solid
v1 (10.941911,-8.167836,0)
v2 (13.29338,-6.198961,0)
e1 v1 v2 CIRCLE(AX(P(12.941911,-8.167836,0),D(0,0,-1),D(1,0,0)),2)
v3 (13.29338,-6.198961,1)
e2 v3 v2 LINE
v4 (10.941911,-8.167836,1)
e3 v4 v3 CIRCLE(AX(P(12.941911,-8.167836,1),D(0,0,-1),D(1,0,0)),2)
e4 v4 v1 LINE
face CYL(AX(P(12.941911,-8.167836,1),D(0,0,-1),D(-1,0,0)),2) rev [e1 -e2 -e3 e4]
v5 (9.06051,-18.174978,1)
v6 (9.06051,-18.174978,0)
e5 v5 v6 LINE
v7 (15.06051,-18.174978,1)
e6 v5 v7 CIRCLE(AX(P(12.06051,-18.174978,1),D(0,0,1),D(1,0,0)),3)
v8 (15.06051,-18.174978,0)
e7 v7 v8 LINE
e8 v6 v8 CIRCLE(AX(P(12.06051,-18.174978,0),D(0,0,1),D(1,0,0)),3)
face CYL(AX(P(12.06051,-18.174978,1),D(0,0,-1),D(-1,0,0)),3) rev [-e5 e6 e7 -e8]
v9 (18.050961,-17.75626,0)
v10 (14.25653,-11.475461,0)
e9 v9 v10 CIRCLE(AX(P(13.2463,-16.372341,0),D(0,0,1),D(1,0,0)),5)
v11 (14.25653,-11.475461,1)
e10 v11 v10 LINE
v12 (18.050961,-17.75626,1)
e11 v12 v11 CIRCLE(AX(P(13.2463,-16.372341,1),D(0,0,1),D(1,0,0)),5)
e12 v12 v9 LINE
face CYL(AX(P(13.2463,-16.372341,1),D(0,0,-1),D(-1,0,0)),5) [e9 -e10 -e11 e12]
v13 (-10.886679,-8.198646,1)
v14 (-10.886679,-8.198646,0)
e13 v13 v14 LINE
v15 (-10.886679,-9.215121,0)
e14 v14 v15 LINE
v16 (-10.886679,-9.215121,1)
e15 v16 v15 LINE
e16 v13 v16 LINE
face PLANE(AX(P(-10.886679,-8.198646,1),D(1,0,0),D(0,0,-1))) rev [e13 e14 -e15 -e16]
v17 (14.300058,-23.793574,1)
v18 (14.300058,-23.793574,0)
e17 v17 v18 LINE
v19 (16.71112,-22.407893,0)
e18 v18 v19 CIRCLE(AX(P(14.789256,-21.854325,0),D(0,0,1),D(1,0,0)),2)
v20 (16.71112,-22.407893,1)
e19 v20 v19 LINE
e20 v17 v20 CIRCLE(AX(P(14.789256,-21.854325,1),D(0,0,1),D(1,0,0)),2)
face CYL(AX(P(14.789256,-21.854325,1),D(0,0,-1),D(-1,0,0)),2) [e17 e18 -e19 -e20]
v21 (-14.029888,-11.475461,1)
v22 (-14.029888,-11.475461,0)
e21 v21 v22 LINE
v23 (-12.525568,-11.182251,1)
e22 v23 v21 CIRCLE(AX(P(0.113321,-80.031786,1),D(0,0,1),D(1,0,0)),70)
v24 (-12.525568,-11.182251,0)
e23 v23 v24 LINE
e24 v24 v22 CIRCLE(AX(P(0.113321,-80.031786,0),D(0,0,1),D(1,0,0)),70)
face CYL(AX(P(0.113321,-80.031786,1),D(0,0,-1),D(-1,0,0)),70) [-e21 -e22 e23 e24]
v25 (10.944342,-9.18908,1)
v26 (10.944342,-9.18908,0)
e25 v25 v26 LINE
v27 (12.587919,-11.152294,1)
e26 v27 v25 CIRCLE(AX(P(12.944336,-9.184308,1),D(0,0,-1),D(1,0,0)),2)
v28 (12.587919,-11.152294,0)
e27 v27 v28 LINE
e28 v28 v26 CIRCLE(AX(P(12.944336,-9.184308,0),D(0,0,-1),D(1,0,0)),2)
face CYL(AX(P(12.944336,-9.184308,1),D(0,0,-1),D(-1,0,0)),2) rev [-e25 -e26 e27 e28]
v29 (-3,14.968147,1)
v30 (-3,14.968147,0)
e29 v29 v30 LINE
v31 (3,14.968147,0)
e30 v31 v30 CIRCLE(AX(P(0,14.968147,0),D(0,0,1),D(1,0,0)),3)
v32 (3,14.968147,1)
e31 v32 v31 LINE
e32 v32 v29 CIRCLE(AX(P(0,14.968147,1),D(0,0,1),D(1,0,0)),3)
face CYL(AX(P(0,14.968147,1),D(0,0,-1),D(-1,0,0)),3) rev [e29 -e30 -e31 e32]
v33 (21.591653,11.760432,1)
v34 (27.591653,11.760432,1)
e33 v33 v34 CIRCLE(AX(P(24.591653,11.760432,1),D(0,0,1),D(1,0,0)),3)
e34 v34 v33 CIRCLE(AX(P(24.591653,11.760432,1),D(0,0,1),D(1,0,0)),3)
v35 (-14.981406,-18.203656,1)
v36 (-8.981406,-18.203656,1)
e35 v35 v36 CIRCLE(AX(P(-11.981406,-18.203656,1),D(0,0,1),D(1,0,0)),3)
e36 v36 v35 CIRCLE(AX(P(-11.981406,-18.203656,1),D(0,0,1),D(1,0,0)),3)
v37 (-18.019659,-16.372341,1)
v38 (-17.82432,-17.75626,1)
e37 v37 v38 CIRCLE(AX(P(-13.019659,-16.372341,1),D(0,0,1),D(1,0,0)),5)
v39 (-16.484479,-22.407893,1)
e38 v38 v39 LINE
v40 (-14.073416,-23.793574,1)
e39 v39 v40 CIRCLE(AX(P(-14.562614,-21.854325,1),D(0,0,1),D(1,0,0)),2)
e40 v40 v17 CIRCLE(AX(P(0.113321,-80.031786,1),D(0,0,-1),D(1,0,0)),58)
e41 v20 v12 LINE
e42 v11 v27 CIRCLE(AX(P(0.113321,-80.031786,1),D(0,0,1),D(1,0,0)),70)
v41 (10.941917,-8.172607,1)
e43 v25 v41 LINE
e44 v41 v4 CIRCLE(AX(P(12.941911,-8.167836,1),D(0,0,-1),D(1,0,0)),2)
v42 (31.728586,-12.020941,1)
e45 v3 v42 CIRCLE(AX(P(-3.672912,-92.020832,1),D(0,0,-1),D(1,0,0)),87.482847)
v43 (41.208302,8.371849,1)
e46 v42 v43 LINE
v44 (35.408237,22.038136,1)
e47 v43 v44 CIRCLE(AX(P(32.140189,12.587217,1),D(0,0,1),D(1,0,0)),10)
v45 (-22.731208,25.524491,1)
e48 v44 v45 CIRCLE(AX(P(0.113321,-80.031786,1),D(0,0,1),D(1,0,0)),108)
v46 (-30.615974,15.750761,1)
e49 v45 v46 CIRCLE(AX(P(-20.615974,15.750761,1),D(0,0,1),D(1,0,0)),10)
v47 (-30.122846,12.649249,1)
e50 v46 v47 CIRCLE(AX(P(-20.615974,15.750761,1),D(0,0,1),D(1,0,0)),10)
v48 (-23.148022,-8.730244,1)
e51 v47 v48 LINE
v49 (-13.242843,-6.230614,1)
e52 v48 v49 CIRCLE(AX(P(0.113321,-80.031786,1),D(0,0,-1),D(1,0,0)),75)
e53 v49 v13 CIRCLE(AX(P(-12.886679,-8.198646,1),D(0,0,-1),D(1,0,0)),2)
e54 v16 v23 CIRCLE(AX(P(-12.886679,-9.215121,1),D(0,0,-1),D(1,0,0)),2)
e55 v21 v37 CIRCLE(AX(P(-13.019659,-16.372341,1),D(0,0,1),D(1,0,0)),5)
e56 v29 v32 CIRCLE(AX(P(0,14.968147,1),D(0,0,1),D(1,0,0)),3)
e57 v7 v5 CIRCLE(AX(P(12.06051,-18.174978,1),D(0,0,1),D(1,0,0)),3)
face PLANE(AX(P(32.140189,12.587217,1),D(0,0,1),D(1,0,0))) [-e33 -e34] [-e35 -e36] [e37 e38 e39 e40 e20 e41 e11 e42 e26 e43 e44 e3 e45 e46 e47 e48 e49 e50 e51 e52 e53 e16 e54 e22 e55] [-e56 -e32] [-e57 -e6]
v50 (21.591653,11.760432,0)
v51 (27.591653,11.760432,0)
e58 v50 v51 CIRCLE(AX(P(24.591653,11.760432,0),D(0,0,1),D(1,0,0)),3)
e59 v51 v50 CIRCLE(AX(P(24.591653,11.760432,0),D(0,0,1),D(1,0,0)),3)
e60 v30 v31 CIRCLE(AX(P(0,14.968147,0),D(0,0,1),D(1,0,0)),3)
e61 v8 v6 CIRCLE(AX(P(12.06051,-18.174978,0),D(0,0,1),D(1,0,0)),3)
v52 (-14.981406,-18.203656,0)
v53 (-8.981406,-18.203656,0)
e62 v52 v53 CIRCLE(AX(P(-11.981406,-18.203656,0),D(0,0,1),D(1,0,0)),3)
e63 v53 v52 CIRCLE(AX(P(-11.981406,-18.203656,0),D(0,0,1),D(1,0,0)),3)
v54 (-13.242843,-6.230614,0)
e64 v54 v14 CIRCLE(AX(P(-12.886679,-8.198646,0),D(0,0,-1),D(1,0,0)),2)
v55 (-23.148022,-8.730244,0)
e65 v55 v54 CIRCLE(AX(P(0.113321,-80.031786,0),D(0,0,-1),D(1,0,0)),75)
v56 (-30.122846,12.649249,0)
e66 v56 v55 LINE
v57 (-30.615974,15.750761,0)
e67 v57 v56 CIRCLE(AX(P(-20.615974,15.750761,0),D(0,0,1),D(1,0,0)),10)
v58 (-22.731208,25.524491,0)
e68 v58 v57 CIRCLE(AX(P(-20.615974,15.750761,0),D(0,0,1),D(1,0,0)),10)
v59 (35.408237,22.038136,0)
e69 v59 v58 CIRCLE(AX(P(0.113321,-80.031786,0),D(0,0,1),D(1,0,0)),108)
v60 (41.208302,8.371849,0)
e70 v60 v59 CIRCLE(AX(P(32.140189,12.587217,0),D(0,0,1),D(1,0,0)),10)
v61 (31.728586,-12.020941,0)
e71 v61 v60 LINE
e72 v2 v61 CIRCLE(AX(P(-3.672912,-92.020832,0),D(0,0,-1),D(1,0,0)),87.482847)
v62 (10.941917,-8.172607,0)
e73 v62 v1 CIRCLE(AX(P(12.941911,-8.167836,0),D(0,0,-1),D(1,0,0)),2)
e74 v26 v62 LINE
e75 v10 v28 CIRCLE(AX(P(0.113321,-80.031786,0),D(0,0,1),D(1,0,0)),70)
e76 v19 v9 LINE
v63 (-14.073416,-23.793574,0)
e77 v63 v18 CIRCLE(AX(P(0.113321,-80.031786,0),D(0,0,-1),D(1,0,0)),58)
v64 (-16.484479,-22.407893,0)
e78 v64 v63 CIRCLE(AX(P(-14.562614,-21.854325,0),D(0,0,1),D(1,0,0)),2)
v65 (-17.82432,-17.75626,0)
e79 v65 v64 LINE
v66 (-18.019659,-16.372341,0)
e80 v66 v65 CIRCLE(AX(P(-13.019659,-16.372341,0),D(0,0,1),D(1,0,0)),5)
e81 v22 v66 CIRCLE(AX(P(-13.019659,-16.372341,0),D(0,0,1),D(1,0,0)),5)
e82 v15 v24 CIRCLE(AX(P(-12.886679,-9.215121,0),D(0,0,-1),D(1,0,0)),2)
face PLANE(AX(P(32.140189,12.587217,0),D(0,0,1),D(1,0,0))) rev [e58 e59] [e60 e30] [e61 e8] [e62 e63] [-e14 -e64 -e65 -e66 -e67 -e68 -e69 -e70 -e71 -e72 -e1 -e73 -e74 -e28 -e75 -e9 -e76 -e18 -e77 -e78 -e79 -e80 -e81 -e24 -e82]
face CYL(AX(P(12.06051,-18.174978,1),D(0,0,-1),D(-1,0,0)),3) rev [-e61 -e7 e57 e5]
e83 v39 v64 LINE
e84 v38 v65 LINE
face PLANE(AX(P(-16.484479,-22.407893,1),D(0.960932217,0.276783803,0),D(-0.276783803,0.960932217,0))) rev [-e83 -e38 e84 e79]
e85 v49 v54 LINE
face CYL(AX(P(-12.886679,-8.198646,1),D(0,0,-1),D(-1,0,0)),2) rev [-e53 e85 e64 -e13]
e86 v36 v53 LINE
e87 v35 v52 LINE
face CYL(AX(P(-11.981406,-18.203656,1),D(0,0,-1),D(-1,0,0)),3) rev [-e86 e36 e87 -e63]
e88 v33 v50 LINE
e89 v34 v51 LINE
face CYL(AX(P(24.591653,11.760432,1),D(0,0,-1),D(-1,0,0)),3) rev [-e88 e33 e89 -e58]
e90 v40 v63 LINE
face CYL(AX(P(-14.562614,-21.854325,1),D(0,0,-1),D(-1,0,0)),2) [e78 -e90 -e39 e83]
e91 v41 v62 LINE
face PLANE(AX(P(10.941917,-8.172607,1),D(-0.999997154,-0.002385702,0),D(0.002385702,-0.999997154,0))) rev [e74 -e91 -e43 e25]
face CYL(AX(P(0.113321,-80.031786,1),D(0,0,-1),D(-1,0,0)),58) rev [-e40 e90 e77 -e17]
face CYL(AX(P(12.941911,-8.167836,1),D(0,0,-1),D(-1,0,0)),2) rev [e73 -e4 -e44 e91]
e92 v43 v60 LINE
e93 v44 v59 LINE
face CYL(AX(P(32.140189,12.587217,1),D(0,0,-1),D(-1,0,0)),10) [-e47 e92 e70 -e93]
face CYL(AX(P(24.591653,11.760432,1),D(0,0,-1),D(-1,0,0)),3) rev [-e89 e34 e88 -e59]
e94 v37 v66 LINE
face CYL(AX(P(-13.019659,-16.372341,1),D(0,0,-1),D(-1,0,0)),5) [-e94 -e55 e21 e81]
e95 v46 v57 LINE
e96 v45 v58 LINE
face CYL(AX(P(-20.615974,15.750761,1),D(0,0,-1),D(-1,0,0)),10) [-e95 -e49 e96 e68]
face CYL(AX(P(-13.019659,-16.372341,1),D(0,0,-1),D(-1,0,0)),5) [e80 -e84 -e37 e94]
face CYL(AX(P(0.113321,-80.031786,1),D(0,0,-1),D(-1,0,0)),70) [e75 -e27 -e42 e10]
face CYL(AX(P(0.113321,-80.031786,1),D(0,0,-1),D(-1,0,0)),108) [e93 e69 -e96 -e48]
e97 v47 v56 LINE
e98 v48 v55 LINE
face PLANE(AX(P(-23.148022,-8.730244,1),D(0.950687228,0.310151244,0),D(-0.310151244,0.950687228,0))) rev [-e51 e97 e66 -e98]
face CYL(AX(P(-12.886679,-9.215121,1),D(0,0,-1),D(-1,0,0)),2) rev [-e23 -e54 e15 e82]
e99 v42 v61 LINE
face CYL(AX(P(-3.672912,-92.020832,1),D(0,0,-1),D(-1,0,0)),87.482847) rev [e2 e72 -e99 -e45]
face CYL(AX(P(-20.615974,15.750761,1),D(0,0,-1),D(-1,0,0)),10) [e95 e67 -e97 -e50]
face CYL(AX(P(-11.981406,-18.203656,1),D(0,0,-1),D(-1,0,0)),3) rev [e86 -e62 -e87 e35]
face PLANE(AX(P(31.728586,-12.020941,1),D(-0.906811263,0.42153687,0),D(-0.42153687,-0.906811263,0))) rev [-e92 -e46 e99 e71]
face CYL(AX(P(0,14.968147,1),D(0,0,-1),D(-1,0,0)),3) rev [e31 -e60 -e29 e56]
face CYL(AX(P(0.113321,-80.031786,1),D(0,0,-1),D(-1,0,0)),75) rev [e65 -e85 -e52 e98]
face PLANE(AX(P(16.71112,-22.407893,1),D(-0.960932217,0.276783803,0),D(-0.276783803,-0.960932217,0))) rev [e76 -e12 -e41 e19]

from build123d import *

# Parameters (mm, degrees)
SKETCH1_R           = 3
BOSS_EXTRUDE2_DEPTH = 1


with BuildPart() as part:
    # Sketch1 → Boss-Extrude2 (new body)
    with BuildSketch(Plane.XY):
        with BuildLine():
            Line((-23.148022373, -8.730243593), (-30.122846489, 12.649248922))
            ThreePointArc((-30.122846489, 12.649248922), (-29.288419203, 20.729586307), (-22.731208407, 25.524490657))
            ThreePointArc((-22.731208407, 25.524490657), (6.577970793, 27.774560597), (35.408236715, 22.038136022))
            ThreePointArc((35.408236715, 22.038136022), (41.345462771, 16.493997865), (41.208301592, 8.371848645))
            Line((41.208301592, 8.371848645), (31.728586192, -12.020940954))
            ThreePointArc((31.728586192, -12.020940954), (22.672300426, -8.599141601), (13.293379688, -6.198960674))
            ThreePointArc((13.293379688, -6.198960674), (11.656131568, -6.635918882), (10.941917146, -8.172607413))
            Line((10.941917146, -8.172607413), (10.944342154, -9.189079799))
            ThreePointArc((10.944342154, -9.189079799), (11.410804247, -10.468161557), (12.587919364, -11.152293875))
            ThreePointArc((12.587919364, -11.152293875), (13.423205338, -11.308812996), (14.256529596, -11.475461055))
            ThreePointArc((14.256529596, -11.475461055), (17.525943772, -13.786871862), (18.050961494, -17.7562604))
            Line((18.050961494, -17.7562604), (16.711120416, -22.40789263))
            ThreePointArc((16.711120416, -22.40789263), (15.785830822, -23.588348839), (14.300058147, -23.793573714))
            ThreePointArc((14.300058147, -23.793573714), (0.113320945, -22.031785702), (-14.073416257, -23.793573714))
            ThreePointArc((-14.073416257, -23.793573714), (-15.559188932, -23.588348839), (-16.484478526, -22.40789263))
            Line((-16.484478526, -22.40789263), (-17.824319603, -17.7562604))
            ThreePointArc((-17.824319603, -17.7562604), (-17.299301882, -13.786871862), (-14.029887705, -11.475461055))
            ThreePointArc((-14.029887705, -11.475461055), (-13.278530318, -11.324738612), (-12.525567944, -11.182250571))
            ThreePointArc((-12.525567944, -11.182250571), (-11.350088312, -10.495311954), (-10.886679055, -9.215120996))
            Line((-10.886679055, -9.215120996), (-10.886679055, -8.198645717))
            ThreePointArc((-10.886679055, -8.198645717), (-11.604557525, -6.663665462), (-13.242843438, -6.230614485))
            ThreePointArc((-13.242843438, -6.230614485), (-18.238041511, -7.311585647), (-23.148022373, -8.730243593))
        make_face()
        with Locations((12.060510133, -18.174977907)):
            Circle(SKETCH1_R, mode=Mode.SUBTRACT)
        with Locations((-11.981406179, -18.203656377)):
            Circle(SKETCH1_R, mode=Mode.SUBTRACT)
        with Locations((0, 14.968146711)):
            Circle(SKETCH1_R, mode=Mode.SUBTRACT)
        with Locations((24.591653109, 11.76043213)):
            Circle(SKETCH1_R, mode=Mode.SUBTRACT)
    extrude(amount=BOSS_EXTRUDE2_DEPTH)


solid = part.part
